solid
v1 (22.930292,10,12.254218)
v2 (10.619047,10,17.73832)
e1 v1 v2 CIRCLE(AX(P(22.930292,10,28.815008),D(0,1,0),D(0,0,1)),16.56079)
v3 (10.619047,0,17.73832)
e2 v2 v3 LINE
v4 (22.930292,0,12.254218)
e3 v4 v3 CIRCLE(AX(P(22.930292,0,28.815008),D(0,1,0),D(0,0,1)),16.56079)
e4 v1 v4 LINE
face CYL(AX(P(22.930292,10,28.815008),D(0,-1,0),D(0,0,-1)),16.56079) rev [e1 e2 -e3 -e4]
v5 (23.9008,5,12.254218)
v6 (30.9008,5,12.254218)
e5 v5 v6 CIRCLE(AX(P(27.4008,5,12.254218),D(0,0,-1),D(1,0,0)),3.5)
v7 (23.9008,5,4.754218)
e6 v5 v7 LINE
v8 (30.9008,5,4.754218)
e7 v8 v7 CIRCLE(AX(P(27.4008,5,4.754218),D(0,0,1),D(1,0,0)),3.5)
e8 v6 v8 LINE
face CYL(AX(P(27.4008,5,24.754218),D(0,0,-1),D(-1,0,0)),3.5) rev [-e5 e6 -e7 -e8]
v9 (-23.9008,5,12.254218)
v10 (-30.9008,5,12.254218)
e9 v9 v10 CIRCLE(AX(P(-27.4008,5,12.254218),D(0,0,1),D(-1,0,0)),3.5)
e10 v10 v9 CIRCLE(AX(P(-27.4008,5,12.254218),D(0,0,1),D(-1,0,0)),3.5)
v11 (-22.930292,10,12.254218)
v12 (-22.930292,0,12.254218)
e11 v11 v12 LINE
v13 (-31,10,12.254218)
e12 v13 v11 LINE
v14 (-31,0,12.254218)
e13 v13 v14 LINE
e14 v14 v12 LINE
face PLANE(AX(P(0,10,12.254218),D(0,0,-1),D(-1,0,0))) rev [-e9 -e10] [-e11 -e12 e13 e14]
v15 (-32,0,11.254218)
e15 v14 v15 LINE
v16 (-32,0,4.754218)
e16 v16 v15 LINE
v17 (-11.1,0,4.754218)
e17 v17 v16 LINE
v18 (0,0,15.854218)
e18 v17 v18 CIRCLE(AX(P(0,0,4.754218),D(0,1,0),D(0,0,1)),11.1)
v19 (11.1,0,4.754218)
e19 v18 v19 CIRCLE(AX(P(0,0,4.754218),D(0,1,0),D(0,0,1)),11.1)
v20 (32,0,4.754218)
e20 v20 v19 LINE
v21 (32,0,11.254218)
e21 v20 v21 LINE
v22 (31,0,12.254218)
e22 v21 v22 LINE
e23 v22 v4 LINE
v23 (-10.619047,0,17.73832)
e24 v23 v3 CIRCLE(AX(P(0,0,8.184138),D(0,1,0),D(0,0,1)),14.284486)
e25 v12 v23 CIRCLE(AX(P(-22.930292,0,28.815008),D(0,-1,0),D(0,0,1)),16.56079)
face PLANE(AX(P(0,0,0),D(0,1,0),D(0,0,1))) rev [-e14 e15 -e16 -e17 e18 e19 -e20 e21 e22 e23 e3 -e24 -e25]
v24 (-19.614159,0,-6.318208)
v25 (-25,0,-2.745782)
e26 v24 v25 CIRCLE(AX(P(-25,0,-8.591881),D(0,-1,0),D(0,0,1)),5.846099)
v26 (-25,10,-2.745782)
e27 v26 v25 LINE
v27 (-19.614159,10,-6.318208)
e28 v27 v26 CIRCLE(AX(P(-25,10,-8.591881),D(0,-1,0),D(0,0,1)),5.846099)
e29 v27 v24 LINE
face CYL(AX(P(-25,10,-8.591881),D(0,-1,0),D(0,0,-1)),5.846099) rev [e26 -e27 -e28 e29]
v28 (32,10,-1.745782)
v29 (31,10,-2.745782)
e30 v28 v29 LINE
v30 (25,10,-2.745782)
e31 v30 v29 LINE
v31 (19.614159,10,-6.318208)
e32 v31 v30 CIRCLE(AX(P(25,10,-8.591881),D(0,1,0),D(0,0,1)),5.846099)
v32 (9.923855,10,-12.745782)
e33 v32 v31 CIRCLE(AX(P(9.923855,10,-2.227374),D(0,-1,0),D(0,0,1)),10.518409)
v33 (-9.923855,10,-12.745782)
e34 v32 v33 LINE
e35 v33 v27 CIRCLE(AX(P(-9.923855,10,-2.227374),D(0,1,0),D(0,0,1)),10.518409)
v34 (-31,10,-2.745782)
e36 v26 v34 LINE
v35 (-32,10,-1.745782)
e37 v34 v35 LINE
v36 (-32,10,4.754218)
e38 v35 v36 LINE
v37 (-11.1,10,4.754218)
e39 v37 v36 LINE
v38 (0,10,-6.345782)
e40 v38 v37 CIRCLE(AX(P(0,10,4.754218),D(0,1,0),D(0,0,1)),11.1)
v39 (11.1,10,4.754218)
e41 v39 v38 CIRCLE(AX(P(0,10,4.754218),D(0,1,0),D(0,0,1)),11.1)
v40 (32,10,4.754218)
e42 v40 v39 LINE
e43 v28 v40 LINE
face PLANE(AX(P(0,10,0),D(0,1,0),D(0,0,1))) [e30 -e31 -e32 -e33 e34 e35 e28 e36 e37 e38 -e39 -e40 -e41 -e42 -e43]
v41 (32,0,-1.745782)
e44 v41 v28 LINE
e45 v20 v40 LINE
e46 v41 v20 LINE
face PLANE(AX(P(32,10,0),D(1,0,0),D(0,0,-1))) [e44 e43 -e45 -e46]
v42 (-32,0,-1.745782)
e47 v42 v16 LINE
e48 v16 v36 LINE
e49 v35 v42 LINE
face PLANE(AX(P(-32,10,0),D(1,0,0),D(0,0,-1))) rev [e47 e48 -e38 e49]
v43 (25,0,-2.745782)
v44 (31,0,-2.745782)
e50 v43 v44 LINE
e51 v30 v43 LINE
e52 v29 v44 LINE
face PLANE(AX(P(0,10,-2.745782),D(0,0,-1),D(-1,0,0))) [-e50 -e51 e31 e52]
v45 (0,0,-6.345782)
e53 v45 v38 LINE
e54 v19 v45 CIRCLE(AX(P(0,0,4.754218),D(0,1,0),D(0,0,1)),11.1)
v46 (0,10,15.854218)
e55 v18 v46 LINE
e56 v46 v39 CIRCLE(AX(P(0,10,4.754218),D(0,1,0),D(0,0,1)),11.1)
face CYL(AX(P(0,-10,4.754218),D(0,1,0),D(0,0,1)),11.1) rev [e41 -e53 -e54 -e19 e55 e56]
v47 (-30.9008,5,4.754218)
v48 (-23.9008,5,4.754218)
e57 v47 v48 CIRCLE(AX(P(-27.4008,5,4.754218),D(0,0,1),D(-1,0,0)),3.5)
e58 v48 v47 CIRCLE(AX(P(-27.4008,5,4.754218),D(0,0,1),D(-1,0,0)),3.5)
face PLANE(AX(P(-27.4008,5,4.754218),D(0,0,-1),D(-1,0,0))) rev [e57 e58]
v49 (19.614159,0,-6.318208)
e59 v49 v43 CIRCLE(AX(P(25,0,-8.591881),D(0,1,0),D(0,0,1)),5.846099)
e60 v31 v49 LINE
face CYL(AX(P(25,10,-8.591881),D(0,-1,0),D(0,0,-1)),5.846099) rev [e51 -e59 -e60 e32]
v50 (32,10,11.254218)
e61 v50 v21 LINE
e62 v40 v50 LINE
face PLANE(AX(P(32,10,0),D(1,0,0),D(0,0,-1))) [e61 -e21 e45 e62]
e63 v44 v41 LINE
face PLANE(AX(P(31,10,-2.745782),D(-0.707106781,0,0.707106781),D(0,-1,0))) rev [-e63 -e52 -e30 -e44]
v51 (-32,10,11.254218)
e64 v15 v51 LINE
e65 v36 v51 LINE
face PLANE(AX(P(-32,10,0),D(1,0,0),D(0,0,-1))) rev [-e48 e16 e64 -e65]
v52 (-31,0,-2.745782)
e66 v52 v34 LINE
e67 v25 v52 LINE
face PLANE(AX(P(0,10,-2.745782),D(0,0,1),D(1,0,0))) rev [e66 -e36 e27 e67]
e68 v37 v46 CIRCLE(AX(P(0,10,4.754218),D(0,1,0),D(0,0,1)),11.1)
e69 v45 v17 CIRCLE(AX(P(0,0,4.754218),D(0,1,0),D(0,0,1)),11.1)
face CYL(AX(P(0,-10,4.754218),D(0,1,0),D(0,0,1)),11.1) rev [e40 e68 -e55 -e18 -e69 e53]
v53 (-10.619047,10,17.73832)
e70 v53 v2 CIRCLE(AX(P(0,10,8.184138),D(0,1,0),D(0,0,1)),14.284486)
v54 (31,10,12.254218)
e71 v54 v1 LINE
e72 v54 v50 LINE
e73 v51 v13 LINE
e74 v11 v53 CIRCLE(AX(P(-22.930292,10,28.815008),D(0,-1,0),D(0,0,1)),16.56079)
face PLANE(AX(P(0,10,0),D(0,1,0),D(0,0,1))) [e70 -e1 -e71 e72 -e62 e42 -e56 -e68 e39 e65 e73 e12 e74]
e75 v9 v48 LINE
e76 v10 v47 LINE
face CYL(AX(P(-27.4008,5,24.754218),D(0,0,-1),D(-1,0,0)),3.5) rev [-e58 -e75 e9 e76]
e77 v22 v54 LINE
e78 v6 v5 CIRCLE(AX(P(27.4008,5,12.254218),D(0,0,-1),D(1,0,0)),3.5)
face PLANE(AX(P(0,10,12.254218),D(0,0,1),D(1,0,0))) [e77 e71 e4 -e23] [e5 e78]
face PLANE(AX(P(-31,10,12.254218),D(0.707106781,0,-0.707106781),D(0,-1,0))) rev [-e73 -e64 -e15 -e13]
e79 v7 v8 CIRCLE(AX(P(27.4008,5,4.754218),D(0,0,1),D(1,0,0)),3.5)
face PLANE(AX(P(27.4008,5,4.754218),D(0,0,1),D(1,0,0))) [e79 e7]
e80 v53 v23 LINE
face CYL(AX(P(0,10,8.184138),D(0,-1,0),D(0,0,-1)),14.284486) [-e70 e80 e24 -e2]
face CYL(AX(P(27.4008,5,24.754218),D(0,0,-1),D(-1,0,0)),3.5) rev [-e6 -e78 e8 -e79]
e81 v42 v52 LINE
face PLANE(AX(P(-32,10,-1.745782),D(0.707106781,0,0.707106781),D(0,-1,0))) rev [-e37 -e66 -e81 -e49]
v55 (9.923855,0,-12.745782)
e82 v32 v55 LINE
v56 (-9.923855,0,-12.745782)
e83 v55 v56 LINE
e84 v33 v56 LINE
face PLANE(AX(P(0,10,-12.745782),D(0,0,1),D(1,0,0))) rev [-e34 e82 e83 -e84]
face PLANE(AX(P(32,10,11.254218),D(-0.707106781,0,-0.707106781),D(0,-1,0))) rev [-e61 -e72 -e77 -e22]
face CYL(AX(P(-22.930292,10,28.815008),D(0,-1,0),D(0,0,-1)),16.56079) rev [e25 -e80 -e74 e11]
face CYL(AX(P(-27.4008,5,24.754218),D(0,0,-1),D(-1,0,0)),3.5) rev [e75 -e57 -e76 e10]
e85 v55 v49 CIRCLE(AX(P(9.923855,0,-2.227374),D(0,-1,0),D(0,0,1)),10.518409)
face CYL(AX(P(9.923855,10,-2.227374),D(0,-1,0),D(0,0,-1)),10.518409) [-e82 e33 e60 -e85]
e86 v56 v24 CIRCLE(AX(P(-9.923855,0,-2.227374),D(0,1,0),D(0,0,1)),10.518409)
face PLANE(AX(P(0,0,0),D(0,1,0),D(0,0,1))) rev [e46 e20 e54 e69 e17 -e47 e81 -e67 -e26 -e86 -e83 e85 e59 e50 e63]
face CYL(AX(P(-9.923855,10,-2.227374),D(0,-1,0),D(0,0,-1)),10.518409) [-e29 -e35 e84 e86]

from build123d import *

# Parameters (mm, degrees)
BOSS_EXTRUDE1_DEPTH = 10
CHAMFER1_SIZE       = 1
CUT_EXTRUDE1_START  = 4.754218
SKETCH3_R           = 3.5
CUT_EXTRUDE1_DEPTH  = 20
SKETCH7_R           = 11.1
CUT_EXTRUDE2_DEPTH  = 20


with BuildPart() as part:
    # Sketch1 → Boss-Extrude1 (new body)
    with BuildSketch(Plane(origin=(0, 0, 0), x_dir=(1, 0, 0), z_dir=(0, 1, 0))):
        with BuildLine():
            Line((9.923855052, 12.745782203), (-9.923855052, 12.745782203))
            ThreePointArc((-9.923855052, 12.745782203), (-15.7379694, 10.992816749), (-19.614159094, 6.318207995))
            ThreePointArc((-19.614159094, 6.318207995), (-21.768533293, 3.720074961), (-25, 2.745782203))
            Line((-25, 2.745782203), (-32, 2.745782203))
            Line((-32, 2.745782203), (-32, -12.254217797))
            Line((-32, -12.254217797), (-22.930291583, -12.254217797))
            ThreePointArc((-22.930291583, -12.254217797), (-16.191557905, -13.687244076), (-10.619046633, -17.738319737))
            ThreePointArc((-10.619046633, -17.738319737), (0, -22.468623982), (10.619046633, -17.738319737))
            ThreePointArc((10.619046633, -17.738319737), (16.191557905, -13.687244076), (22.930291583, -12.254217797))
            Line((22.930291583, -12.254217797), (32, -12.254217797))
            Line((32, -12.254217797), (32, 2.745782203))
            Line((32, 2.745782203), (25, 2.745782203))
            ThreePointArc((25, 2.745782203), (21.768533293, 3.720074961), (19.614159094, 6.318207995))
            ThreePointArc((19.614159094, 6.318207995), (15.7379694, 10.992816749), (9.923855052, 12.745782203))
        make_face()
    extrude(amount=BOSS_EXTRUDE1_DEPTH)

    # Chamfer1
    chamfer1_edges = [part.edges().sort_by_distance(p)[0] for p in [
        (32, 5, -2.745782203),
        (32, 5, 12.254217797),
        (-32, 5, 12.254217797),
        (-32, 5, -2.745782203),
    ]]
    chamfer(chamfer1_edges, length=CHAMFER1_SIZE)

    # Sketch3 → Cut-Extrude1 (cut)
    with BuildSketch(Plane.XY.offset(CUT_EXTRUDE1_START)):
        with Locations((27.40080015, 5)):
            Circle(SKETCH3_R)
        with Locations(Location((-27.40080015, 5, 0), (0, 0, 180))):
            Circle(SKETCH3_R)
    extrude(amount=CUT_EXTRUDE1_DEPTH, mode=Mode.SUBTRACT)

    # Sketch7 → Cut-Extrude2 (cut)
    with BuildSketch(Plane(origin=(0, 10, 0), x_dir=(1, 0, 0), z_dir=(0, 1, 0))):
        with Locations(Location((0, -4.754217797, 0), (0, 0, 180))):
            Circle(SKETCH7_R)
    extrude(amount=-CUT_EXTRUDE2_DEPTH, mode=Mode.SUBTRACT)


solid = part.part
